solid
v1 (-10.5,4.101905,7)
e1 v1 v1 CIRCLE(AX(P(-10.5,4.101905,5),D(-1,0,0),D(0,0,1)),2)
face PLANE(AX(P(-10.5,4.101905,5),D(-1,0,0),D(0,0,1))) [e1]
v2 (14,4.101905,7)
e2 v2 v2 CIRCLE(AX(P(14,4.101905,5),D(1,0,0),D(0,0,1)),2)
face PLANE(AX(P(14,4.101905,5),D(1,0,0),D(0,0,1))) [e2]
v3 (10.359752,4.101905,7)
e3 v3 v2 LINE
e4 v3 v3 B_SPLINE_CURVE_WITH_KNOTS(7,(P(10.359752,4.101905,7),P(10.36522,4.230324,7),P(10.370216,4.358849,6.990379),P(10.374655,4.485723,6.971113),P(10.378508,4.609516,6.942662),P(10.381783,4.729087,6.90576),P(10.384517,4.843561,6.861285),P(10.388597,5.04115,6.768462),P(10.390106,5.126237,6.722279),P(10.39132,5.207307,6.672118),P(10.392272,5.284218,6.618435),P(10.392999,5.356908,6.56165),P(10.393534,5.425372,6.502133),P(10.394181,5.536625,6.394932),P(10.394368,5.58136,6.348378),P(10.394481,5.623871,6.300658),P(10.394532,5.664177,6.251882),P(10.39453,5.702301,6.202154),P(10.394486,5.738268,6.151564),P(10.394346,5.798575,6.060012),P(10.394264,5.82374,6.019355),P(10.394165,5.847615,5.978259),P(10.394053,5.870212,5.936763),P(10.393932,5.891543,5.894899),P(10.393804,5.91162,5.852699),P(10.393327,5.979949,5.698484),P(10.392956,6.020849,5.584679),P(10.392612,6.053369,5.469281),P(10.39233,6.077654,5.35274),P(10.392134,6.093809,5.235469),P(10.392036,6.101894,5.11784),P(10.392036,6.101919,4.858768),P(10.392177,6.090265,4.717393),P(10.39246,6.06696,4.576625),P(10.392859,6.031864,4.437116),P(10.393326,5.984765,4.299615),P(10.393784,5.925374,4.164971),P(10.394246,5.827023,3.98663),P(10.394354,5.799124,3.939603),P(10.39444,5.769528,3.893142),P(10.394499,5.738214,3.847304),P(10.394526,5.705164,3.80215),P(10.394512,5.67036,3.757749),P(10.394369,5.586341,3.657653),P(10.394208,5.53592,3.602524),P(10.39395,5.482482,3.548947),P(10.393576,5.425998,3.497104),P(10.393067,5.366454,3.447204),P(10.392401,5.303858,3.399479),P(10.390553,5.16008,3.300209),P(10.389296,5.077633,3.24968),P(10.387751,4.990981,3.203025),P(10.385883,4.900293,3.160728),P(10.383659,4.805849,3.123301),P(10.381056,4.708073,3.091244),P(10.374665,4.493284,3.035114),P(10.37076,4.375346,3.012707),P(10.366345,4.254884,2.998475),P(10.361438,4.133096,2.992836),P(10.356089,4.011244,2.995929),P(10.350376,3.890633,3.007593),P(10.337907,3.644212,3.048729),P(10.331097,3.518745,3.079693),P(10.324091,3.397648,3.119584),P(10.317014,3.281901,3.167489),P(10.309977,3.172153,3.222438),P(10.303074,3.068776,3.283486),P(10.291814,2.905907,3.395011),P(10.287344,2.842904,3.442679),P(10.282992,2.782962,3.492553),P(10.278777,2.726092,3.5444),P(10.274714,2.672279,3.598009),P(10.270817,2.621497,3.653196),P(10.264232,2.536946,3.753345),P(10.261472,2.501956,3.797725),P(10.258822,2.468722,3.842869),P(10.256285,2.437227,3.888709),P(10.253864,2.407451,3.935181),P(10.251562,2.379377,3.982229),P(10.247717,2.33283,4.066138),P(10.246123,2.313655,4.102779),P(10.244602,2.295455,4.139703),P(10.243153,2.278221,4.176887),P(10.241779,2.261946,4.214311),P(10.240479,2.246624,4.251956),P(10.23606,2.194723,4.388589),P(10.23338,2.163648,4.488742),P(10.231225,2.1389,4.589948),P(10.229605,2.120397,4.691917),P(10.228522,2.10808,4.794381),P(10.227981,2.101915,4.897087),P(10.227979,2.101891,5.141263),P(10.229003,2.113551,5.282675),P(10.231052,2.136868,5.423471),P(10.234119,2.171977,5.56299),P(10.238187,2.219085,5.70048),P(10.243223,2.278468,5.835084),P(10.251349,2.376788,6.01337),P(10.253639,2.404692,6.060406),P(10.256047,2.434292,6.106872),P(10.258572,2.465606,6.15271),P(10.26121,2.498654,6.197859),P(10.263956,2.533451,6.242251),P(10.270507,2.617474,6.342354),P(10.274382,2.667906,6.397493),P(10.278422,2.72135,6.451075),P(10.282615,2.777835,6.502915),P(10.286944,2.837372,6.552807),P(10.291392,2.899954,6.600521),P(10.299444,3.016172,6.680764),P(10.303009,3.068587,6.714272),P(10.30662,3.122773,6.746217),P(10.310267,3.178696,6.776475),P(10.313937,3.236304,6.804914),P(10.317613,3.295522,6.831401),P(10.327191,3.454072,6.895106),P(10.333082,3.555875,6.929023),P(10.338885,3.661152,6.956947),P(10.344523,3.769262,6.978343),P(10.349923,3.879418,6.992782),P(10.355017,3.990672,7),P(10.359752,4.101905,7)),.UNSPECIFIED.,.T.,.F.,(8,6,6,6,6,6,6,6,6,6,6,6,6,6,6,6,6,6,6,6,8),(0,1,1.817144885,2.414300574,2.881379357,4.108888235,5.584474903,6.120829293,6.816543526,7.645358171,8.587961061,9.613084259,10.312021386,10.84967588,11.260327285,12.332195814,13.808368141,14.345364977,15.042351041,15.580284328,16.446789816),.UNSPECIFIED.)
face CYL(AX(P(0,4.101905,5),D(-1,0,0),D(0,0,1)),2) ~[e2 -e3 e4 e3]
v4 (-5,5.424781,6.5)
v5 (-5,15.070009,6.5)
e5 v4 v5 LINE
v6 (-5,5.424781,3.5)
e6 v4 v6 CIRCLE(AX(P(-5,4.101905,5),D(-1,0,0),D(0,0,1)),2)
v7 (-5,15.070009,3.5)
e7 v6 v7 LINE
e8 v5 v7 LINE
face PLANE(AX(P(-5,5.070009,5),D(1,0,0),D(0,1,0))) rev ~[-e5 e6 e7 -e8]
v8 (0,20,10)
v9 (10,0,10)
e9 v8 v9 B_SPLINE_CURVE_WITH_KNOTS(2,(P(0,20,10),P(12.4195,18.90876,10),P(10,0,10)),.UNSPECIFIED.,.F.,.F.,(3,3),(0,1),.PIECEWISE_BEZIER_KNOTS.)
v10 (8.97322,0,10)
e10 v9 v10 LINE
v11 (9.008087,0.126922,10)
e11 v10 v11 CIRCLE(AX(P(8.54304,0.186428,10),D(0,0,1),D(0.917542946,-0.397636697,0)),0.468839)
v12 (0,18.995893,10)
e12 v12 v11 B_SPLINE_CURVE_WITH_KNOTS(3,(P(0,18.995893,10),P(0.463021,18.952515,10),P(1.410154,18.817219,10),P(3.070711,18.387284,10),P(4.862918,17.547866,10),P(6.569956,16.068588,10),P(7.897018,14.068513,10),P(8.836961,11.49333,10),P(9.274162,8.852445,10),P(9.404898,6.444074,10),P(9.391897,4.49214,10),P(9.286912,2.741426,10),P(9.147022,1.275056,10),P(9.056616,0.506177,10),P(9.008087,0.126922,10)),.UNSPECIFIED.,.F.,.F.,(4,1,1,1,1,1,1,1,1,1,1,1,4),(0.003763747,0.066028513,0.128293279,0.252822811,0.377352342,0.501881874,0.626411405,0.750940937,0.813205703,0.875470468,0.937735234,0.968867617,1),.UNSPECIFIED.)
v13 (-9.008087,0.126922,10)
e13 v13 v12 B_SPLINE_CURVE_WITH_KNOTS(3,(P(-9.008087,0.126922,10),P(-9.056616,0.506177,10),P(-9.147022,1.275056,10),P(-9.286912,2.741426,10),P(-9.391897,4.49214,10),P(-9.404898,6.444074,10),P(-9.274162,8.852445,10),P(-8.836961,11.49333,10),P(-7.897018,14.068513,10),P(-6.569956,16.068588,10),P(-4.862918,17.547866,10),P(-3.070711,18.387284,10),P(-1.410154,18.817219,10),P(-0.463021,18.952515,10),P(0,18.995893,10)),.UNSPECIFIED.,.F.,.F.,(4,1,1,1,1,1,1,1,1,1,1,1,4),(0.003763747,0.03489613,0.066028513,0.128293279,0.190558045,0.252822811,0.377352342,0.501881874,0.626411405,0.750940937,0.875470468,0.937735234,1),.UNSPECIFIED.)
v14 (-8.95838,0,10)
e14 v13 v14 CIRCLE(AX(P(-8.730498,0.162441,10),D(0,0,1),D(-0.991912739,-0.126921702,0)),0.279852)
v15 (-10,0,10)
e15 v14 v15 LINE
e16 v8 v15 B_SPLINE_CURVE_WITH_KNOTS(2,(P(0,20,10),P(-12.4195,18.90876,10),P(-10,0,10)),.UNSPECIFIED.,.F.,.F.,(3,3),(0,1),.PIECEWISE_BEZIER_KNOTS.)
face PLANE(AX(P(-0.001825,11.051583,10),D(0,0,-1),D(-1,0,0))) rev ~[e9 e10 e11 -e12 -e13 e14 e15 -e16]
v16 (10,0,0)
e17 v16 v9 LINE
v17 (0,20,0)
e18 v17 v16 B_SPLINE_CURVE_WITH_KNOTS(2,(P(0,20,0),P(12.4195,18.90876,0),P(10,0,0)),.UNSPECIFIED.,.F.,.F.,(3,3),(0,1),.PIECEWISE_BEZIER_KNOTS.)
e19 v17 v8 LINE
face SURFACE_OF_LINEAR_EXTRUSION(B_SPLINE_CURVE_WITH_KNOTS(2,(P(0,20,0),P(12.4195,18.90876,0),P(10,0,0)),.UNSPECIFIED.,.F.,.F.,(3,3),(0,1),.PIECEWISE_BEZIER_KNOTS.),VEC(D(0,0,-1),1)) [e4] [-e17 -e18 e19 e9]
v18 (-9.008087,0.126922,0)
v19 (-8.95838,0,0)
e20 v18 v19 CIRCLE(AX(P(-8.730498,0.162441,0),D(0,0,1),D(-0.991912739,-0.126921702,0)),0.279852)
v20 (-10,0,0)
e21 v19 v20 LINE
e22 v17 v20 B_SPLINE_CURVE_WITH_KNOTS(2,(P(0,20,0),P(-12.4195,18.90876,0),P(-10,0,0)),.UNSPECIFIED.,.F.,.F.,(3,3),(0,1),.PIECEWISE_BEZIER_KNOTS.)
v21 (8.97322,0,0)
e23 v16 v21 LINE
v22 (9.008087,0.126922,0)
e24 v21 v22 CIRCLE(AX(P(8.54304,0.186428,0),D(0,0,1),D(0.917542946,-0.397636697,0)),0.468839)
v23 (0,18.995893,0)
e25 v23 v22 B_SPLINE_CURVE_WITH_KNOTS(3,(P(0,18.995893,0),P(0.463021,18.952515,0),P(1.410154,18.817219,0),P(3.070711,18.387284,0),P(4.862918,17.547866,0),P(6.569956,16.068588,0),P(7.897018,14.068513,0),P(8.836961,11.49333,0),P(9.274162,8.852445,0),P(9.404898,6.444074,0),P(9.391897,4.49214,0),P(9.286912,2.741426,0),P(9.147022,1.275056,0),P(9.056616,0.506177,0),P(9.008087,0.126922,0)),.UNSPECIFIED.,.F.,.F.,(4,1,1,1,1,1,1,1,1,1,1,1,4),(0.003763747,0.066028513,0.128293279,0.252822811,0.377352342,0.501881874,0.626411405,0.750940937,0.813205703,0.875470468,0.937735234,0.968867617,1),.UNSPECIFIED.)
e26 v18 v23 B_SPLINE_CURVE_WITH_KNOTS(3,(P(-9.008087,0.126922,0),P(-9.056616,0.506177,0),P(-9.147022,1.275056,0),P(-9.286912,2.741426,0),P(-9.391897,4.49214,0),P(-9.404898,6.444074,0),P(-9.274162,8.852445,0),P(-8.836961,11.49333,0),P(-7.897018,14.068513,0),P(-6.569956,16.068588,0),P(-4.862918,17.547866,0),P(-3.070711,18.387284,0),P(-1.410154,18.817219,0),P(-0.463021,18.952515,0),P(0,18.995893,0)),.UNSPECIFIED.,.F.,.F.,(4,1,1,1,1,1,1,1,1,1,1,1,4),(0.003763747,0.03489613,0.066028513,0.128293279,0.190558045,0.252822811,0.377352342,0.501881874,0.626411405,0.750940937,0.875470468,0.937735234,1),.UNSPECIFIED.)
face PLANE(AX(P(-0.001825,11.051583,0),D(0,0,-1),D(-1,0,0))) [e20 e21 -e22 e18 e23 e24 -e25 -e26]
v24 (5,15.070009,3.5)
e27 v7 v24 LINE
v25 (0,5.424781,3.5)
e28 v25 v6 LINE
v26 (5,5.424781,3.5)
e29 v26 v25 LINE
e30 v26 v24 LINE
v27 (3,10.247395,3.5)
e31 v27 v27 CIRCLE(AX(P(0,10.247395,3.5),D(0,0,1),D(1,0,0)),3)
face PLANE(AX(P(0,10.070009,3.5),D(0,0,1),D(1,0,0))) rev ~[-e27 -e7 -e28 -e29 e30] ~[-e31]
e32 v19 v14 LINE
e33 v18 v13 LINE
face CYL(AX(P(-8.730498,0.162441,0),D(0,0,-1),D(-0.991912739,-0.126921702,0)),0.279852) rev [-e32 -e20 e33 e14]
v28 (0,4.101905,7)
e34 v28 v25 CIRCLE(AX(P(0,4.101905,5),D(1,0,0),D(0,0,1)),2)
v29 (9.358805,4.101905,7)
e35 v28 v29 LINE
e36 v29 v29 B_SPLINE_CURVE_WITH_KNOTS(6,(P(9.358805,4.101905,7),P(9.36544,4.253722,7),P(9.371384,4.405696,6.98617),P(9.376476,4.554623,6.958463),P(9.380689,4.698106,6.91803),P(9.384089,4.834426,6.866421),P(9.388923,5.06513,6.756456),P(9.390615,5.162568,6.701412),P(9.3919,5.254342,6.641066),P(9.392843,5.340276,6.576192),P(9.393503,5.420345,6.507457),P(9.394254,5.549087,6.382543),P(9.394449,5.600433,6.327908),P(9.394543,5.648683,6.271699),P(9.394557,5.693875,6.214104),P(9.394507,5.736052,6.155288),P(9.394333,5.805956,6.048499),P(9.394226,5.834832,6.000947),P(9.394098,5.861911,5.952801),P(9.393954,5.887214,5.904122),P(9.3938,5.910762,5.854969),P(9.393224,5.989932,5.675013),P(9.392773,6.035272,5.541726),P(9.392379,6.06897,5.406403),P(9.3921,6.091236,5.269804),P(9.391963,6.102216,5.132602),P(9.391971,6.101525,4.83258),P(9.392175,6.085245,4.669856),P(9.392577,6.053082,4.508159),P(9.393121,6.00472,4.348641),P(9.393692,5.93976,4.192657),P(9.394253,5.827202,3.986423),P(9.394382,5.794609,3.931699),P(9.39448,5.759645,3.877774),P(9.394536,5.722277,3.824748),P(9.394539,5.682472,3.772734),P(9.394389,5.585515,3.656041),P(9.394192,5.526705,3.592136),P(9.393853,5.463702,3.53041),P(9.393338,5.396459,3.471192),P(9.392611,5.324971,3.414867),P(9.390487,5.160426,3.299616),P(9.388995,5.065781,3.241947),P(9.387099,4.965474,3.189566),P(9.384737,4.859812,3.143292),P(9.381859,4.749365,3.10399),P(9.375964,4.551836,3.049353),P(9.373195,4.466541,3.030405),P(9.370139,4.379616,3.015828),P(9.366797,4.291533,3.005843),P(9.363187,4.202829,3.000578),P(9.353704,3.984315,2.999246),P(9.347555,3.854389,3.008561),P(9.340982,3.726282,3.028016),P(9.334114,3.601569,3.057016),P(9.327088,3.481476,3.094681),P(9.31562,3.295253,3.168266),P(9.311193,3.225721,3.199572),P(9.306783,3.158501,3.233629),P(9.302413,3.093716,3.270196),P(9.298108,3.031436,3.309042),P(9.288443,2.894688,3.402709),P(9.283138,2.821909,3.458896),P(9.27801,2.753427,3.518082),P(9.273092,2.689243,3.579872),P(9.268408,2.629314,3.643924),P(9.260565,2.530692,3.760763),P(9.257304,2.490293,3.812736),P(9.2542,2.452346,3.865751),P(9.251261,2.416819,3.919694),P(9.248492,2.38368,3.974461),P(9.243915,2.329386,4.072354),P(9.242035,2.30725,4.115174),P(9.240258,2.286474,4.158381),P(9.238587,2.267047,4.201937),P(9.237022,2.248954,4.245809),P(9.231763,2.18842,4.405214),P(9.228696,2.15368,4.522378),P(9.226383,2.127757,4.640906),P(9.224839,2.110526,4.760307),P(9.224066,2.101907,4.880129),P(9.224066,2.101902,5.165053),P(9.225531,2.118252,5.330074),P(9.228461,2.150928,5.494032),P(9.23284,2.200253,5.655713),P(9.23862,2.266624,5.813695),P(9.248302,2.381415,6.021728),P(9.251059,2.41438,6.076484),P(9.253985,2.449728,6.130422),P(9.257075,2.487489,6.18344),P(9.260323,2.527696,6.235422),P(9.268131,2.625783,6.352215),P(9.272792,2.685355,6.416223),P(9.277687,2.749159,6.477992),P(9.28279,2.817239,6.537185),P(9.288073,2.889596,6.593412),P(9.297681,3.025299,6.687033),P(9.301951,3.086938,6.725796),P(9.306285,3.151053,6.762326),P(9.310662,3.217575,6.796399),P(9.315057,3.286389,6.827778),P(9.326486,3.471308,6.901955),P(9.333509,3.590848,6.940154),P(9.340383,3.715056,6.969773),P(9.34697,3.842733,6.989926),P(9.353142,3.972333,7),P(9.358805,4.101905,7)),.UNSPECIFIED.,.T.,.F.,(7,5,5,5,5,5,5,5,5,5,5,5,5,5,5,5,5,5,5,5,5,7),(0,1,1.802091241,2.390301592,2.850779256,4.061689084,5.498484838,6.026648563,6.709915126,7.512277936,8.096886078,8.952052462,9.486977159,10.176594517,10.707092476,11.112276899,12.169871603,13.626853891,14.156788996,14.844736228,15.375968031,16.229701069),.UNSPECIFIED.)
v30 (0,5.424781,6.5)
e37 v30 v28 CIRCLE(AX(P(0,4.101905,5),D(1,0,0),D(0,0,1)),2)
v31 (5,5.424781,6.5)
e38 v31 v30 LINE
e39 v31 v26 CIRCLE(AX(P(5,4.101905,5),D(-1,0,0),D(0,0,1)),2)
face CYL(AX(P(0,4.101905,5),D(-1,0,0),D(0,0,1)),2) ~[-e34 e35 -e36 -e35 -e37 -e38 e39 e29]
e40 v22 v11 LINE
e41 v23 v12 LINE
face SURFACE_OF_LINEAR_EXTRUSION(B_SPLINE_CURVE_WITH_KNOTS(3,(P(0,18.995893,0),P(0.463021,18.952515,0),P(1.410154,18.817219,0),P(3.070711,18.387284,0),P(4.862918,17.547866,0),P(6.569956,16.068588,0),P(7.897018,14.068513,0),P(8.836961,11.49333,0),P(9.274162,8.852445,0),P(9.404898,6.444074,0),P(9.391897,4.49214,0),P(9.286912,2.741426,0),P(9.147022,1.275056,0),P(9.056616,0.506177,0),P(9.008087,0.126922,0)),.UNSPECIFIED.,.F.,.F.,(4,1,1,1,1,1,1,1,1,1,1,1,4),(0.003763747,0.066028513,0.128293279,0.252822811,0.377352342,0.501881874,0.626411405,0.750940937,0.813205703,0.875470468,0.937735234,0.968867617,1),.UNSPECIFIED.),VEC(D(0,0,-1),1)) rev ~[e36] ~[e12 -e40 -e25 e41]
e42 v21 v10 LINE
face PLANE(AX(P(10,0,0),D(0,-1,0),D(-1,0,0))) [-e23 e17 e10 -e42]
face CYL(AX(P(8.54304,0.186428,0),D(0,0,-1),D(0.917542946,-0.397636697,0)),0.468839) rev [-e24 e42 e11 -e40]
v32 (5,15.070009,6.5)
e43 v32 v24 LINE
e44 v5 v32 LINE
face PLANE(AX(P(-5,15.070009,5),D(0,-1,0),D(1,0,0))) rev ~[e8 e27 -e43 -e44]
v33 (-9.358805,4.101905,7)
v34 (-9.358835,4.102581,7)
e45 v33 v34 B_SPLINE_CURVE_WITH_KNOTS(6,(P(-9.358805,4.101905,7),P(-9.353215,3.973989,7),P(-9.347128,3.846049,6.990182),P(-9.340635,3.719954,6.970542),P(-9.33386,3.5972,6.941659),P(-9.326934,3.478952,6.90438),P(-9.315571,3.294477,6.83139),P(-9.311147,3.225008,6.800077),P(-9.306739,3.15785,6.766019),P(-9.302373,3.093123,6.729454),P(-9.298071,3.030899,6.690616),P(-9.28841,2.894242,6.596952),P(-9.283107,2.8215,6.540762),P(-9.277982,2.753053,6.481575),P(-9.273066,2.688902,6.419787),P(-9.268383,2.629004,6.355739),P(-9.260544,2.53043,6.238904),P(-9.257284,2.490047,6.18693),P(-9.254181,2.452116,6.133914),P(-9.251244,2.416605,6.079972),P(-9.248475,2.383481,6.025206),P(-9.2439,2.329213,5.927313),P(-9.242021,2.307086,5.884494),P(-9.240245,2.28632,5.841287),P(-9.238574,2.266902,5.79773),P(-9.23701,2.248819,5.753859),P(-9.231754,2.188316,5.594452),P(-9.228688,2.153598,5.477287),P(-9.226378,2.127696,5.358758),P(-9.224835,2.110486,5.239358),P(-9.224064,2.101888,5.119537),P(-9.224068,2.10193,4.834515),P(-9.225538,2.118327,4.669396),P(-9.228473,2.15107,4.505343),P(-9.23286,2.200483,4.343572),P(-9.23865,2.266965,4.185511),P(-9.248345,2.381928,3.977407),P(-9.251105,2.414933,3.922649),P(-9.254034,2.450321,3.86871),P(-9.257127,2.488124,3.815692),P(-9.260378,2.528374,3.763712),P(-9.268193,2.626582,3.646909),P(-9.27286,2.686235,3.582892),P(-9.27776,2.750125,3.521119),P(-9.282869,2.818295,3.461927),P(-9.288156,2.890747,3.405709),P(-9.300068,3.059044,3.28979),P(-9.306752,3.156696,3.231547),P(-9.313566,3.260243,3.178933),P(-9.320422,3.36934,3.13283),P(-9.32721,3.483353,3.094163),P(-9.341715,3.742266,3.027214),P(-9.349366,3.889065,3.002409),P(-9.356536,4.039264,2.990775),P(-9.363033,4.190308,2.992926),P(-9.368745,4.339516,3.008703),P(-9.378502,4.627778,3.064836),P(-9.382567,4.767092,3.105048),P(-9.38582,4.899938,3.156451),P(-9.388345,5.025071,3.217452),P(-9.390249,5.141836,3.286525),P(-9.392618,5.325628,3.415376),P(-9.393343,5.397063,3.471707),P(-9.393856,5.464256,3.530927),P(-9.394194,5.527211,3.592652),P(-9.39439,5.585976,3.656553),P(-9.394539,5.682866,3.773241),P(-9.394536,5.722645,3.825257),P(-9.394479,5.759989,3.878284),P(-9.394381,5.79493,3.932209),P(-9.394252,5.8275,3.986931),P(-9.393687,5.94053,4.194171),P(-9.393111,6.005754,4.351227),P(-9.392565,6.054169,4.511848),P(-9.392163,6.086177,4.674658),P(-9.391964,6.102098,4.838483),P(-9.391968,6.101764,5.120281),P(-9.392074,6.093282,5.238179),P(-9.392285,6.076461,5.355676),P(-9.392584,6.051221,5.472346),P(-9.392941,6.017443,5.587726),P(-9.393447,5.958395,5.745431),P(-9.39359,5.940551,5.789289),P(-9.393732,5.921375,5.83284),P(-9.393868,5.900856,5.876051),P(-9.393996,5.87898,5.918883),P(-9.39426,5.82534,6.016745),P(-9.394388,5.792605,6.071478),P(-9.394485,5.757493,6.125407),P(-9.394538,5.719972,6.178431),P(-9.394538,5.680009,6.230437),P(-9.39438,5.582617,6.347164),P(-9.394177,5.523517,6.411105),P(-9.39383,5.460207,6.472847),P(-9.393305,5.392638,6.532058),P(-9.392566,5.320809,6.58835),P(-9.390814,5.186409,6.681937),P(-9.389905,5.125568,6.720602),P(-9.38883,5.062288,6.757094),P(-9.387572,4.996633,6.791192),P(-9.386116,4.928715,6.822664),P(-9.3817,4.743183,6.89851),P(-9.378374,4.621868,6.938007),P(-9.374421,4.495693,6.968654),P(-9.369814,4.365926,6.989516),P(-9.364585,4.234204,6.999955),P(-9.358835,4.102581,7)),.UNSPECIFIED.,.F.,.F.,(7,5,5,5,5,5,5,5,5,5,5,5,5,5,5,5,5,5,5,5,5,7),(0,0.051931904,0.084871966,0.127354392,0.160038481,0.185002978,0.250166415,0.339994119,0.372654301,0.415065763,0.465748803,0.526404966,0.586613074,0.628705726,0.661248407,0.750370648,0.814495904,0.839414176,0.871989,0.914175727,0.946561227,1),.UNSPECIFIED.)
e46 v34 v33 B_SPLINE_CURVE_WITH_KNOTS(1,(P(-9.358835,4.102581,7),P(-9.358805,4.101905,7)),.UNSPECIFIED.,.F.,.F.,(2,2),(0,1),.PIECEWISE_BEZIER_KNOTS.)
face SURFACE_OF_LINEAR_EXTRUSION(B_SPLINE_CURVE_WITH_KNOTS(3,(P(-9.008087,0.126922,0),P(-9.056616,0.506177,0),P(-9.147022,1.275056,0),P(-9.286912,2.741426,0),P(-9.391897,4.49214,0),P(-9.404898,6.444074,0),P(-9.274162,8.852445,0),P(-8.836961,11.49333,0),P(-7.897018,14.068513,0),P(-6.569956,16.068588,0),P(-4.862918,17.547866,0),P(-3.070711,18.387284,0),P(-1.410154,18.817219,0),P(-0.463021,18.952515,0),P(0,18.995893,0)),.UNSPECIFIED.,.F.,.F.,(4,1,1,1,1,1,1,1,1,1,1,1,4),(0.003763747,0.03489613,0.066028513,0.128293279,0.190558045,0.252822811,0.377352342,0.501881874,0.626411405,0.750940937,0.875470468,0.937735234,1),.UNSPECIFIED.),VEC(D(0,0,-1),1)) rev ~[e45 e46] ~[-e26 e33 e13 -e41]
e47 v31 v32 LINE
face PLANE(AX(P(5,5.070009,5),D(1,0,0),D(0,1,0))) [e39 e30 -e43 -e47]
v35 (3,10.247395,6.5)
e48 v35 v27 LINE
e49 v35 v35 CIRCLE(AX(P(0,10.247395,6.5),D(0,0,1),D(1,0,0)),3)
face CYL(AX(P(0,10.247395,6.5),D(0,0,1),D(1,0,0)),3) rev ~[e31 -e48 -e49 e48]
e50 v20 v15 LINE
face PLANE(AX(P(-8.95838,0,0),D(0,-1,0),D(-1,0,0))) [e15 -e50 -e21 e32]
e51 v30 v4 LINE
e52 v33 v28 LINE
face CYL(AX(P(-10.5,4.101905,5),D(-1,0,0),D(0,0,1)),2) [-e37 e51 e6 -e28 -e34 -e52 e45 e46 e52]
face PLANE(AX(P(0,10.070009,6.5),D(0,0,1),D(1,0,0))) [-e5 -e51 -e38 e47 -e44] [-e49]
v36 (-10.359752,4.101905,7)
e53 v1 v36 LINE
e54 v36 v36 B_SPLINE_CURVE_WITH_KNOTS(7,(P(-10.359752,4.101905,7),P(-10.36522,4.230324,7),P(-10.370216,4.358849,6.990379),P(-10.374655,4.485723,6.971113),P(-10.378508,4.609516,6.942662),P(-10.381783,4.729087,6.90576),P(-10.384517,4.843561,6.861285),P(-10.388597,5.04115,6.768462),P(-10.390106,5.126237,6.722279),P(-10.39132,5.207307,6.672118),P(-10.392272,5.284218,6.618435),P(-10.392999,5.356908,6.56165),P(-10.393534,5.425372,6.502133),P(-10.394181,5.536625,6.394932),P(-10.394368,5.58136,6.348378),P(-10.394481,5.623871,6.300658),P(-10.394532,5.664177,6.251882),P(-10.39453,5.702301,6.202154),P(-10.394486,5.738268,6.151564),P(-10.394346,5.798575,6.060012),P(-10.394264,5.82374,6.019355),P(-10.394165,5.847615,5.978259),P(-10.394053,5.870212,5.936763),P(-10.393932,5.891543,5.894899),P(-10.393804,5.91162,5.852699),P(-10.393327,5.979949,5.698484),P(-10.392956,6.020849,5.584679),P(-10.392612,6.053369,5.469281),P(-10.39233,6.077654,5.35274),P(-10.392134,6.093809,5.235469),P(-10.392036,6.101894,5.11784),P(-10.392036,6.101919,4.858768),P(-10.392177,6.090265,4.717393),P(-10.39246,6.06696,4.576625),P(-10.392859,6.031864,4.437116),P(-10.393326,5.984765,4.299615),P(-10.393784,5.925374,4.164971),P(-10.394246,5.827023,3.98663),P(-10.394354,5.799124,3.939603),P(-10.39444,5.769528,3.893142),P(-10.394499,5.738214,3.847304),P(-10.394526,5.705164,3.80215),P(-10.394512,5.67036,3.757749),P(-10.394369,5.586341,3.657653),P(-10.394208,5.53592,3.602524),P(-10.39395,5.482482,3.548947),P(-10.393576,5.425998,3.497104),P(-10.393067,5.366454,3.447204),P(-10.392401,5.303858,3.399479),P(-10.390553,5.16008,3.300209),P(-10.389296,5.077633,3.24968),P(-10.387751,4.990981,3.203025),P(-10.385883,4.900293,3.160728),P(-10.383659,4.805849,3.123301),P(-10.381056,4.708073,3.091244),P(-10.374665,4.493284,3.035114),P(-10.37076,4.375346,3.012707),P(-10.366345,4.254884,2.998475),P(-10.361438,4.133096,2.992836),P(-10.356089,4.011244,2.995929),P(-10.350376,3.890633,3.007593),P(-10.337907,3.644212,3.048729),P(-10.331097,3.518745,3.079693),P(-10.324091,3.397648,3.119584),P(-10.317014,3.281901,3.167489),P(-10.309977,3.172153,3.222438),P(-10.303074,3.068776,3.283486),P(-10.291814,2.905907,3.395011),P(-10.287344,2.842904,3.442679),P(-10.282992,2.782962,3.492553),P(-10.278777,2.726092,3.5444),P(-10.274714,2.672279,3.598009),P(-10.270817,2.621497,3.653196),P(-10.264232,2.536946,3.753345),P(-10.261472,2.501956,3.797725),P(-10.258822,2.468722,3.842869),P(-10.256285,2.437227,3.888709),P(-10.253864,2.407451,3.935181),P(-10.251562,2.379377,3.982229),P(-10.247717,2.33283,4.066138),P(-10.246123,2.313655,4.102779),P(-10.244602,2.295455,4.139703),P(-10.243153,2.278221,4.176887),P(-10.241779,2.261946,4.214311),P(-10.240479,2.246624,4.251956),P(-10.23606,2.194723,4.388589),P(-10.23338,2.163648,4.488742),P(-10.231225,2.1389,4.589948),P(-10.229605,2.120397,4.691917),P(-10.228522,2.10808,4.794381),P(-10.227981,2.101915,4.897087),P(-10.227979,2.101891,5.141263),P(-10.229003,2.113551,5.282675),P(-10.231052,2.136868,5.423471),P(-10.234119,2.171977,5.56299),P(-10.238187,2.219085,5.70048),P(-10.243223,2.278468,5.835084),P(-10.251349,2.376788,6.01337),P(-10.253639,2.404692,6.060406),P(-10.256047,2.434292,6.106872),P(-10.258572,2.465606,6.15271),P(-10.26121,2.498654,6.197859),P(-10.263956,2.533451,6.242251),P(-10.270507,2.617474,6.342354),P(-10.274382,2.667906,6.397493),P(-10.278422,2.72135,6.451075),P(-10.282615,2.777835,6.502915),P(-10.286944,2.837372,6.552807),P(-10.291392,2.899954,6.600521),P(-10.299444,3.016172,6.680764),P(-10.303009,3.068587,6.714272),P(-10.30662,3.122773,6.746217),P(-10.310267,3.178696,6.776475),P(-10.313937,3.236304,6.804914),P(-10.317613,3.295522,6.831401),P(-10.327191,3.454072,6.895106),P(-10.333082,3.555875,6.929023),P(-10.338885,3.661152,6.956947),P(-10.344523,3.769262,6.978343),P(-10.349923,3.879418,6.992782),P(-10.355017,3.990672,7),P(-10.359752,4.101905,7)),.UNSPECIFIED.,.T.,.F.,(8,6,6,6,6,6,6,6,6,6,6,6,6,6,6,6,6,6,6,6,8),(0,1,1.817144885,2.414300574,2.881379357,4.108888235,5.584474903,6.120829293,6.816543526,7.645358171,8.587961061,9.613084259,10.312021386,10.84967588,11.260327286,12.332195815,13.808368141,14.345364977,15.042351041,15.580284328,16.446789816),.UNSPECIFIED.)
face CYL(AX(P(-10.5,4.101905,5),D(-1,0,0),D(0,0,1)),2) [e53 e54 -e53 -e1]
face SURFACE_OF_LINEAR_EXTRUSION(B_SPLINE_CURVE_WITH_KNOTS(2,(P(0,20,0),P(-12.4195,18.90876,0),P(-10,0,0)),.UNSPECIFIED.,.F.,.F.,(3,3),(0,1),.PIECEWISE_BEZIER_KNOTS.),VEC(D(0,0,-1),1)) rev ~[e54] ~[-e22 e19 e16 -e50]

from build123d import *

# Parameters (mm, degrees)
BOSS_EXTRUDE1_DEPTH = 10
SKETCH3_R           = 2
BOSS_EXTRUDE2_DEPTH = 14
BOSS_EXTRUDE3_START = 10.5
SKETCH4_R           = 2
BOSS_EXTRUDE3_DEPTH = 10.5
SKETCH5_W           = 10
SKETCH5_H           = 10
BOSS_EXTRUDE4_DEPTH = 1.5
SKETCH6_R           = 3
CUT_EXTRUDE1_DEPTH  = 17


with BuildPart() as part:
    # Sketch1 → Boss-Extrude1 (new body)
    with BuildSketch(Plane.XY):
        with BuildLine():
            Line((10, 0), (8.973219811, 0))
            ThreePointArc((8.973219811, 0), (8.995129769, 0.062231167), (9.008087263, 0.12692172))
            add(Edge.make_bspline(
                [(0, 18.99589315), (0.463021411, 18.952514541), (1.410153528, 18.817218931), (3.070711392, 18.387284064), (4.862917757, 17.547866349), (6.569955551, 16.068587591), (7.897017979, 14.068512915), (8.836960927, 11.493329945), (9.27416213, 8.852445104), (9.404897772, 6.444073782), (9.391897127, 4.492140022), (9.286912223, 2.741425841), (9.147022016, 1.275055797), (9.056615507, 0.506177397), (9.008087263, 0.12692172)],
                knots=[0.003763747, 0.003763747, 0.003763747, 0.003763747, 0.066028513, 0.128293279, 0.252822811, 0.377352342, 0.501881874, 0.626411405, 0.750940937, 0.813205703, 0.875470468, 0.937735234, 0.968867617, 1, 1, 1, 1], degree=3))
            add(Edge.make_bspline(
                [(-9.008087263, 0.12692172), (-9.056615507, 0.506177397), (-9.147022016, 1.275055797), (-9.286912223, 2.741425841), (-9.391897127, 4.492140022), (-9.404897772, 6.444073782), (-9.27416213, 8.852445104), (-8.836960927, 11.493329945), (-7.897017979, 14.068512915), (-6.569955551, 16.068587591), (-4.862917757, 17.547866349), (-3.070711392, 18.387284064), (-1.410153528, 18.817218931), (-0.463021411, 18.952514541), (0, 18.99589315)],
                knots=[0.003763747, 0.003763747, 0.003763747, 0.003763747, 0.03489613, 0.066028513, 0.128293279, 0.190558045, 0.252822811, 0.377352342, 0.501881874, 0.626411405, 0.750940937, 0.875470468, 0.937735234, 1, 1, 1, 1], degree=3))
            ThreePointArc((-9.008087263, 0.12692172), (-8.991079354, 0.060388246), (-8.958380239, 0))
            Line((-8.958380239, 0), (-10, 0))
            add(Edge.make_bspline(
                [(0, 20), (-12.419499504, 18.908760189), (-10, 0)],
                knots=[0, 0, 0, 1, 1, 1], degree=2))
            add(Edge.make_bspline(
                [(0, 20), (12.419499504, 18.908760189), (10, 0)],
                knots=[0, 0, 0, 1, 1, 1], degree=2))
        make_face()
    extrude(amount=BOSS_EXTRUDE1_DEPTH)

    # Sketch3 → Boss-Extrude2 (add)
    with BuildSketch(Plane(origin=(0, 0, 0), x_dir=(0, 0, -1), z_dir=(1, 0, 0))):
        with Locations(Location((-5, 4.101905217, 0), (0, 0, 180))):
            Circle(SKETCH3_R)
    extrude(amount=BOSS_EXTRUDE2_DEPTH)

    # Sketch4 → Boss-Extrude3 (add)
    with BuildSketch(Plane.ZY.offset(BOSS_EXTRUDE3_START)):
        with Locations((5, 4.101905217)):
            Circle(SKETCH4_R)
    extrude(amount=-BOSS_EXTRUDE3_DEPTH)

    # Sketch5 → Boss-Extrude4 (add, symmetric)
    with BuildSketch(Plane.XY.offset(5)):
        with Locations((0, 10.070009498)):
            Rectangle(SKETCH5_W, SKETCH5_H)
    extrude(amount=BOSS_EXTRUDE4_DEPTH, both=True)

    # Sketch6 → Cut-Extrude1 (cut)
    with BuildSketch(Plane.XY.offset(6.5)):
        with Locations((0, 10.247395185)):
            Circle(SKETCH6_R)
    extrude(amount=-CUT_EXTRUDE1_DEPTH, mode=Mode.SUBTRACT)


solid = part.part
